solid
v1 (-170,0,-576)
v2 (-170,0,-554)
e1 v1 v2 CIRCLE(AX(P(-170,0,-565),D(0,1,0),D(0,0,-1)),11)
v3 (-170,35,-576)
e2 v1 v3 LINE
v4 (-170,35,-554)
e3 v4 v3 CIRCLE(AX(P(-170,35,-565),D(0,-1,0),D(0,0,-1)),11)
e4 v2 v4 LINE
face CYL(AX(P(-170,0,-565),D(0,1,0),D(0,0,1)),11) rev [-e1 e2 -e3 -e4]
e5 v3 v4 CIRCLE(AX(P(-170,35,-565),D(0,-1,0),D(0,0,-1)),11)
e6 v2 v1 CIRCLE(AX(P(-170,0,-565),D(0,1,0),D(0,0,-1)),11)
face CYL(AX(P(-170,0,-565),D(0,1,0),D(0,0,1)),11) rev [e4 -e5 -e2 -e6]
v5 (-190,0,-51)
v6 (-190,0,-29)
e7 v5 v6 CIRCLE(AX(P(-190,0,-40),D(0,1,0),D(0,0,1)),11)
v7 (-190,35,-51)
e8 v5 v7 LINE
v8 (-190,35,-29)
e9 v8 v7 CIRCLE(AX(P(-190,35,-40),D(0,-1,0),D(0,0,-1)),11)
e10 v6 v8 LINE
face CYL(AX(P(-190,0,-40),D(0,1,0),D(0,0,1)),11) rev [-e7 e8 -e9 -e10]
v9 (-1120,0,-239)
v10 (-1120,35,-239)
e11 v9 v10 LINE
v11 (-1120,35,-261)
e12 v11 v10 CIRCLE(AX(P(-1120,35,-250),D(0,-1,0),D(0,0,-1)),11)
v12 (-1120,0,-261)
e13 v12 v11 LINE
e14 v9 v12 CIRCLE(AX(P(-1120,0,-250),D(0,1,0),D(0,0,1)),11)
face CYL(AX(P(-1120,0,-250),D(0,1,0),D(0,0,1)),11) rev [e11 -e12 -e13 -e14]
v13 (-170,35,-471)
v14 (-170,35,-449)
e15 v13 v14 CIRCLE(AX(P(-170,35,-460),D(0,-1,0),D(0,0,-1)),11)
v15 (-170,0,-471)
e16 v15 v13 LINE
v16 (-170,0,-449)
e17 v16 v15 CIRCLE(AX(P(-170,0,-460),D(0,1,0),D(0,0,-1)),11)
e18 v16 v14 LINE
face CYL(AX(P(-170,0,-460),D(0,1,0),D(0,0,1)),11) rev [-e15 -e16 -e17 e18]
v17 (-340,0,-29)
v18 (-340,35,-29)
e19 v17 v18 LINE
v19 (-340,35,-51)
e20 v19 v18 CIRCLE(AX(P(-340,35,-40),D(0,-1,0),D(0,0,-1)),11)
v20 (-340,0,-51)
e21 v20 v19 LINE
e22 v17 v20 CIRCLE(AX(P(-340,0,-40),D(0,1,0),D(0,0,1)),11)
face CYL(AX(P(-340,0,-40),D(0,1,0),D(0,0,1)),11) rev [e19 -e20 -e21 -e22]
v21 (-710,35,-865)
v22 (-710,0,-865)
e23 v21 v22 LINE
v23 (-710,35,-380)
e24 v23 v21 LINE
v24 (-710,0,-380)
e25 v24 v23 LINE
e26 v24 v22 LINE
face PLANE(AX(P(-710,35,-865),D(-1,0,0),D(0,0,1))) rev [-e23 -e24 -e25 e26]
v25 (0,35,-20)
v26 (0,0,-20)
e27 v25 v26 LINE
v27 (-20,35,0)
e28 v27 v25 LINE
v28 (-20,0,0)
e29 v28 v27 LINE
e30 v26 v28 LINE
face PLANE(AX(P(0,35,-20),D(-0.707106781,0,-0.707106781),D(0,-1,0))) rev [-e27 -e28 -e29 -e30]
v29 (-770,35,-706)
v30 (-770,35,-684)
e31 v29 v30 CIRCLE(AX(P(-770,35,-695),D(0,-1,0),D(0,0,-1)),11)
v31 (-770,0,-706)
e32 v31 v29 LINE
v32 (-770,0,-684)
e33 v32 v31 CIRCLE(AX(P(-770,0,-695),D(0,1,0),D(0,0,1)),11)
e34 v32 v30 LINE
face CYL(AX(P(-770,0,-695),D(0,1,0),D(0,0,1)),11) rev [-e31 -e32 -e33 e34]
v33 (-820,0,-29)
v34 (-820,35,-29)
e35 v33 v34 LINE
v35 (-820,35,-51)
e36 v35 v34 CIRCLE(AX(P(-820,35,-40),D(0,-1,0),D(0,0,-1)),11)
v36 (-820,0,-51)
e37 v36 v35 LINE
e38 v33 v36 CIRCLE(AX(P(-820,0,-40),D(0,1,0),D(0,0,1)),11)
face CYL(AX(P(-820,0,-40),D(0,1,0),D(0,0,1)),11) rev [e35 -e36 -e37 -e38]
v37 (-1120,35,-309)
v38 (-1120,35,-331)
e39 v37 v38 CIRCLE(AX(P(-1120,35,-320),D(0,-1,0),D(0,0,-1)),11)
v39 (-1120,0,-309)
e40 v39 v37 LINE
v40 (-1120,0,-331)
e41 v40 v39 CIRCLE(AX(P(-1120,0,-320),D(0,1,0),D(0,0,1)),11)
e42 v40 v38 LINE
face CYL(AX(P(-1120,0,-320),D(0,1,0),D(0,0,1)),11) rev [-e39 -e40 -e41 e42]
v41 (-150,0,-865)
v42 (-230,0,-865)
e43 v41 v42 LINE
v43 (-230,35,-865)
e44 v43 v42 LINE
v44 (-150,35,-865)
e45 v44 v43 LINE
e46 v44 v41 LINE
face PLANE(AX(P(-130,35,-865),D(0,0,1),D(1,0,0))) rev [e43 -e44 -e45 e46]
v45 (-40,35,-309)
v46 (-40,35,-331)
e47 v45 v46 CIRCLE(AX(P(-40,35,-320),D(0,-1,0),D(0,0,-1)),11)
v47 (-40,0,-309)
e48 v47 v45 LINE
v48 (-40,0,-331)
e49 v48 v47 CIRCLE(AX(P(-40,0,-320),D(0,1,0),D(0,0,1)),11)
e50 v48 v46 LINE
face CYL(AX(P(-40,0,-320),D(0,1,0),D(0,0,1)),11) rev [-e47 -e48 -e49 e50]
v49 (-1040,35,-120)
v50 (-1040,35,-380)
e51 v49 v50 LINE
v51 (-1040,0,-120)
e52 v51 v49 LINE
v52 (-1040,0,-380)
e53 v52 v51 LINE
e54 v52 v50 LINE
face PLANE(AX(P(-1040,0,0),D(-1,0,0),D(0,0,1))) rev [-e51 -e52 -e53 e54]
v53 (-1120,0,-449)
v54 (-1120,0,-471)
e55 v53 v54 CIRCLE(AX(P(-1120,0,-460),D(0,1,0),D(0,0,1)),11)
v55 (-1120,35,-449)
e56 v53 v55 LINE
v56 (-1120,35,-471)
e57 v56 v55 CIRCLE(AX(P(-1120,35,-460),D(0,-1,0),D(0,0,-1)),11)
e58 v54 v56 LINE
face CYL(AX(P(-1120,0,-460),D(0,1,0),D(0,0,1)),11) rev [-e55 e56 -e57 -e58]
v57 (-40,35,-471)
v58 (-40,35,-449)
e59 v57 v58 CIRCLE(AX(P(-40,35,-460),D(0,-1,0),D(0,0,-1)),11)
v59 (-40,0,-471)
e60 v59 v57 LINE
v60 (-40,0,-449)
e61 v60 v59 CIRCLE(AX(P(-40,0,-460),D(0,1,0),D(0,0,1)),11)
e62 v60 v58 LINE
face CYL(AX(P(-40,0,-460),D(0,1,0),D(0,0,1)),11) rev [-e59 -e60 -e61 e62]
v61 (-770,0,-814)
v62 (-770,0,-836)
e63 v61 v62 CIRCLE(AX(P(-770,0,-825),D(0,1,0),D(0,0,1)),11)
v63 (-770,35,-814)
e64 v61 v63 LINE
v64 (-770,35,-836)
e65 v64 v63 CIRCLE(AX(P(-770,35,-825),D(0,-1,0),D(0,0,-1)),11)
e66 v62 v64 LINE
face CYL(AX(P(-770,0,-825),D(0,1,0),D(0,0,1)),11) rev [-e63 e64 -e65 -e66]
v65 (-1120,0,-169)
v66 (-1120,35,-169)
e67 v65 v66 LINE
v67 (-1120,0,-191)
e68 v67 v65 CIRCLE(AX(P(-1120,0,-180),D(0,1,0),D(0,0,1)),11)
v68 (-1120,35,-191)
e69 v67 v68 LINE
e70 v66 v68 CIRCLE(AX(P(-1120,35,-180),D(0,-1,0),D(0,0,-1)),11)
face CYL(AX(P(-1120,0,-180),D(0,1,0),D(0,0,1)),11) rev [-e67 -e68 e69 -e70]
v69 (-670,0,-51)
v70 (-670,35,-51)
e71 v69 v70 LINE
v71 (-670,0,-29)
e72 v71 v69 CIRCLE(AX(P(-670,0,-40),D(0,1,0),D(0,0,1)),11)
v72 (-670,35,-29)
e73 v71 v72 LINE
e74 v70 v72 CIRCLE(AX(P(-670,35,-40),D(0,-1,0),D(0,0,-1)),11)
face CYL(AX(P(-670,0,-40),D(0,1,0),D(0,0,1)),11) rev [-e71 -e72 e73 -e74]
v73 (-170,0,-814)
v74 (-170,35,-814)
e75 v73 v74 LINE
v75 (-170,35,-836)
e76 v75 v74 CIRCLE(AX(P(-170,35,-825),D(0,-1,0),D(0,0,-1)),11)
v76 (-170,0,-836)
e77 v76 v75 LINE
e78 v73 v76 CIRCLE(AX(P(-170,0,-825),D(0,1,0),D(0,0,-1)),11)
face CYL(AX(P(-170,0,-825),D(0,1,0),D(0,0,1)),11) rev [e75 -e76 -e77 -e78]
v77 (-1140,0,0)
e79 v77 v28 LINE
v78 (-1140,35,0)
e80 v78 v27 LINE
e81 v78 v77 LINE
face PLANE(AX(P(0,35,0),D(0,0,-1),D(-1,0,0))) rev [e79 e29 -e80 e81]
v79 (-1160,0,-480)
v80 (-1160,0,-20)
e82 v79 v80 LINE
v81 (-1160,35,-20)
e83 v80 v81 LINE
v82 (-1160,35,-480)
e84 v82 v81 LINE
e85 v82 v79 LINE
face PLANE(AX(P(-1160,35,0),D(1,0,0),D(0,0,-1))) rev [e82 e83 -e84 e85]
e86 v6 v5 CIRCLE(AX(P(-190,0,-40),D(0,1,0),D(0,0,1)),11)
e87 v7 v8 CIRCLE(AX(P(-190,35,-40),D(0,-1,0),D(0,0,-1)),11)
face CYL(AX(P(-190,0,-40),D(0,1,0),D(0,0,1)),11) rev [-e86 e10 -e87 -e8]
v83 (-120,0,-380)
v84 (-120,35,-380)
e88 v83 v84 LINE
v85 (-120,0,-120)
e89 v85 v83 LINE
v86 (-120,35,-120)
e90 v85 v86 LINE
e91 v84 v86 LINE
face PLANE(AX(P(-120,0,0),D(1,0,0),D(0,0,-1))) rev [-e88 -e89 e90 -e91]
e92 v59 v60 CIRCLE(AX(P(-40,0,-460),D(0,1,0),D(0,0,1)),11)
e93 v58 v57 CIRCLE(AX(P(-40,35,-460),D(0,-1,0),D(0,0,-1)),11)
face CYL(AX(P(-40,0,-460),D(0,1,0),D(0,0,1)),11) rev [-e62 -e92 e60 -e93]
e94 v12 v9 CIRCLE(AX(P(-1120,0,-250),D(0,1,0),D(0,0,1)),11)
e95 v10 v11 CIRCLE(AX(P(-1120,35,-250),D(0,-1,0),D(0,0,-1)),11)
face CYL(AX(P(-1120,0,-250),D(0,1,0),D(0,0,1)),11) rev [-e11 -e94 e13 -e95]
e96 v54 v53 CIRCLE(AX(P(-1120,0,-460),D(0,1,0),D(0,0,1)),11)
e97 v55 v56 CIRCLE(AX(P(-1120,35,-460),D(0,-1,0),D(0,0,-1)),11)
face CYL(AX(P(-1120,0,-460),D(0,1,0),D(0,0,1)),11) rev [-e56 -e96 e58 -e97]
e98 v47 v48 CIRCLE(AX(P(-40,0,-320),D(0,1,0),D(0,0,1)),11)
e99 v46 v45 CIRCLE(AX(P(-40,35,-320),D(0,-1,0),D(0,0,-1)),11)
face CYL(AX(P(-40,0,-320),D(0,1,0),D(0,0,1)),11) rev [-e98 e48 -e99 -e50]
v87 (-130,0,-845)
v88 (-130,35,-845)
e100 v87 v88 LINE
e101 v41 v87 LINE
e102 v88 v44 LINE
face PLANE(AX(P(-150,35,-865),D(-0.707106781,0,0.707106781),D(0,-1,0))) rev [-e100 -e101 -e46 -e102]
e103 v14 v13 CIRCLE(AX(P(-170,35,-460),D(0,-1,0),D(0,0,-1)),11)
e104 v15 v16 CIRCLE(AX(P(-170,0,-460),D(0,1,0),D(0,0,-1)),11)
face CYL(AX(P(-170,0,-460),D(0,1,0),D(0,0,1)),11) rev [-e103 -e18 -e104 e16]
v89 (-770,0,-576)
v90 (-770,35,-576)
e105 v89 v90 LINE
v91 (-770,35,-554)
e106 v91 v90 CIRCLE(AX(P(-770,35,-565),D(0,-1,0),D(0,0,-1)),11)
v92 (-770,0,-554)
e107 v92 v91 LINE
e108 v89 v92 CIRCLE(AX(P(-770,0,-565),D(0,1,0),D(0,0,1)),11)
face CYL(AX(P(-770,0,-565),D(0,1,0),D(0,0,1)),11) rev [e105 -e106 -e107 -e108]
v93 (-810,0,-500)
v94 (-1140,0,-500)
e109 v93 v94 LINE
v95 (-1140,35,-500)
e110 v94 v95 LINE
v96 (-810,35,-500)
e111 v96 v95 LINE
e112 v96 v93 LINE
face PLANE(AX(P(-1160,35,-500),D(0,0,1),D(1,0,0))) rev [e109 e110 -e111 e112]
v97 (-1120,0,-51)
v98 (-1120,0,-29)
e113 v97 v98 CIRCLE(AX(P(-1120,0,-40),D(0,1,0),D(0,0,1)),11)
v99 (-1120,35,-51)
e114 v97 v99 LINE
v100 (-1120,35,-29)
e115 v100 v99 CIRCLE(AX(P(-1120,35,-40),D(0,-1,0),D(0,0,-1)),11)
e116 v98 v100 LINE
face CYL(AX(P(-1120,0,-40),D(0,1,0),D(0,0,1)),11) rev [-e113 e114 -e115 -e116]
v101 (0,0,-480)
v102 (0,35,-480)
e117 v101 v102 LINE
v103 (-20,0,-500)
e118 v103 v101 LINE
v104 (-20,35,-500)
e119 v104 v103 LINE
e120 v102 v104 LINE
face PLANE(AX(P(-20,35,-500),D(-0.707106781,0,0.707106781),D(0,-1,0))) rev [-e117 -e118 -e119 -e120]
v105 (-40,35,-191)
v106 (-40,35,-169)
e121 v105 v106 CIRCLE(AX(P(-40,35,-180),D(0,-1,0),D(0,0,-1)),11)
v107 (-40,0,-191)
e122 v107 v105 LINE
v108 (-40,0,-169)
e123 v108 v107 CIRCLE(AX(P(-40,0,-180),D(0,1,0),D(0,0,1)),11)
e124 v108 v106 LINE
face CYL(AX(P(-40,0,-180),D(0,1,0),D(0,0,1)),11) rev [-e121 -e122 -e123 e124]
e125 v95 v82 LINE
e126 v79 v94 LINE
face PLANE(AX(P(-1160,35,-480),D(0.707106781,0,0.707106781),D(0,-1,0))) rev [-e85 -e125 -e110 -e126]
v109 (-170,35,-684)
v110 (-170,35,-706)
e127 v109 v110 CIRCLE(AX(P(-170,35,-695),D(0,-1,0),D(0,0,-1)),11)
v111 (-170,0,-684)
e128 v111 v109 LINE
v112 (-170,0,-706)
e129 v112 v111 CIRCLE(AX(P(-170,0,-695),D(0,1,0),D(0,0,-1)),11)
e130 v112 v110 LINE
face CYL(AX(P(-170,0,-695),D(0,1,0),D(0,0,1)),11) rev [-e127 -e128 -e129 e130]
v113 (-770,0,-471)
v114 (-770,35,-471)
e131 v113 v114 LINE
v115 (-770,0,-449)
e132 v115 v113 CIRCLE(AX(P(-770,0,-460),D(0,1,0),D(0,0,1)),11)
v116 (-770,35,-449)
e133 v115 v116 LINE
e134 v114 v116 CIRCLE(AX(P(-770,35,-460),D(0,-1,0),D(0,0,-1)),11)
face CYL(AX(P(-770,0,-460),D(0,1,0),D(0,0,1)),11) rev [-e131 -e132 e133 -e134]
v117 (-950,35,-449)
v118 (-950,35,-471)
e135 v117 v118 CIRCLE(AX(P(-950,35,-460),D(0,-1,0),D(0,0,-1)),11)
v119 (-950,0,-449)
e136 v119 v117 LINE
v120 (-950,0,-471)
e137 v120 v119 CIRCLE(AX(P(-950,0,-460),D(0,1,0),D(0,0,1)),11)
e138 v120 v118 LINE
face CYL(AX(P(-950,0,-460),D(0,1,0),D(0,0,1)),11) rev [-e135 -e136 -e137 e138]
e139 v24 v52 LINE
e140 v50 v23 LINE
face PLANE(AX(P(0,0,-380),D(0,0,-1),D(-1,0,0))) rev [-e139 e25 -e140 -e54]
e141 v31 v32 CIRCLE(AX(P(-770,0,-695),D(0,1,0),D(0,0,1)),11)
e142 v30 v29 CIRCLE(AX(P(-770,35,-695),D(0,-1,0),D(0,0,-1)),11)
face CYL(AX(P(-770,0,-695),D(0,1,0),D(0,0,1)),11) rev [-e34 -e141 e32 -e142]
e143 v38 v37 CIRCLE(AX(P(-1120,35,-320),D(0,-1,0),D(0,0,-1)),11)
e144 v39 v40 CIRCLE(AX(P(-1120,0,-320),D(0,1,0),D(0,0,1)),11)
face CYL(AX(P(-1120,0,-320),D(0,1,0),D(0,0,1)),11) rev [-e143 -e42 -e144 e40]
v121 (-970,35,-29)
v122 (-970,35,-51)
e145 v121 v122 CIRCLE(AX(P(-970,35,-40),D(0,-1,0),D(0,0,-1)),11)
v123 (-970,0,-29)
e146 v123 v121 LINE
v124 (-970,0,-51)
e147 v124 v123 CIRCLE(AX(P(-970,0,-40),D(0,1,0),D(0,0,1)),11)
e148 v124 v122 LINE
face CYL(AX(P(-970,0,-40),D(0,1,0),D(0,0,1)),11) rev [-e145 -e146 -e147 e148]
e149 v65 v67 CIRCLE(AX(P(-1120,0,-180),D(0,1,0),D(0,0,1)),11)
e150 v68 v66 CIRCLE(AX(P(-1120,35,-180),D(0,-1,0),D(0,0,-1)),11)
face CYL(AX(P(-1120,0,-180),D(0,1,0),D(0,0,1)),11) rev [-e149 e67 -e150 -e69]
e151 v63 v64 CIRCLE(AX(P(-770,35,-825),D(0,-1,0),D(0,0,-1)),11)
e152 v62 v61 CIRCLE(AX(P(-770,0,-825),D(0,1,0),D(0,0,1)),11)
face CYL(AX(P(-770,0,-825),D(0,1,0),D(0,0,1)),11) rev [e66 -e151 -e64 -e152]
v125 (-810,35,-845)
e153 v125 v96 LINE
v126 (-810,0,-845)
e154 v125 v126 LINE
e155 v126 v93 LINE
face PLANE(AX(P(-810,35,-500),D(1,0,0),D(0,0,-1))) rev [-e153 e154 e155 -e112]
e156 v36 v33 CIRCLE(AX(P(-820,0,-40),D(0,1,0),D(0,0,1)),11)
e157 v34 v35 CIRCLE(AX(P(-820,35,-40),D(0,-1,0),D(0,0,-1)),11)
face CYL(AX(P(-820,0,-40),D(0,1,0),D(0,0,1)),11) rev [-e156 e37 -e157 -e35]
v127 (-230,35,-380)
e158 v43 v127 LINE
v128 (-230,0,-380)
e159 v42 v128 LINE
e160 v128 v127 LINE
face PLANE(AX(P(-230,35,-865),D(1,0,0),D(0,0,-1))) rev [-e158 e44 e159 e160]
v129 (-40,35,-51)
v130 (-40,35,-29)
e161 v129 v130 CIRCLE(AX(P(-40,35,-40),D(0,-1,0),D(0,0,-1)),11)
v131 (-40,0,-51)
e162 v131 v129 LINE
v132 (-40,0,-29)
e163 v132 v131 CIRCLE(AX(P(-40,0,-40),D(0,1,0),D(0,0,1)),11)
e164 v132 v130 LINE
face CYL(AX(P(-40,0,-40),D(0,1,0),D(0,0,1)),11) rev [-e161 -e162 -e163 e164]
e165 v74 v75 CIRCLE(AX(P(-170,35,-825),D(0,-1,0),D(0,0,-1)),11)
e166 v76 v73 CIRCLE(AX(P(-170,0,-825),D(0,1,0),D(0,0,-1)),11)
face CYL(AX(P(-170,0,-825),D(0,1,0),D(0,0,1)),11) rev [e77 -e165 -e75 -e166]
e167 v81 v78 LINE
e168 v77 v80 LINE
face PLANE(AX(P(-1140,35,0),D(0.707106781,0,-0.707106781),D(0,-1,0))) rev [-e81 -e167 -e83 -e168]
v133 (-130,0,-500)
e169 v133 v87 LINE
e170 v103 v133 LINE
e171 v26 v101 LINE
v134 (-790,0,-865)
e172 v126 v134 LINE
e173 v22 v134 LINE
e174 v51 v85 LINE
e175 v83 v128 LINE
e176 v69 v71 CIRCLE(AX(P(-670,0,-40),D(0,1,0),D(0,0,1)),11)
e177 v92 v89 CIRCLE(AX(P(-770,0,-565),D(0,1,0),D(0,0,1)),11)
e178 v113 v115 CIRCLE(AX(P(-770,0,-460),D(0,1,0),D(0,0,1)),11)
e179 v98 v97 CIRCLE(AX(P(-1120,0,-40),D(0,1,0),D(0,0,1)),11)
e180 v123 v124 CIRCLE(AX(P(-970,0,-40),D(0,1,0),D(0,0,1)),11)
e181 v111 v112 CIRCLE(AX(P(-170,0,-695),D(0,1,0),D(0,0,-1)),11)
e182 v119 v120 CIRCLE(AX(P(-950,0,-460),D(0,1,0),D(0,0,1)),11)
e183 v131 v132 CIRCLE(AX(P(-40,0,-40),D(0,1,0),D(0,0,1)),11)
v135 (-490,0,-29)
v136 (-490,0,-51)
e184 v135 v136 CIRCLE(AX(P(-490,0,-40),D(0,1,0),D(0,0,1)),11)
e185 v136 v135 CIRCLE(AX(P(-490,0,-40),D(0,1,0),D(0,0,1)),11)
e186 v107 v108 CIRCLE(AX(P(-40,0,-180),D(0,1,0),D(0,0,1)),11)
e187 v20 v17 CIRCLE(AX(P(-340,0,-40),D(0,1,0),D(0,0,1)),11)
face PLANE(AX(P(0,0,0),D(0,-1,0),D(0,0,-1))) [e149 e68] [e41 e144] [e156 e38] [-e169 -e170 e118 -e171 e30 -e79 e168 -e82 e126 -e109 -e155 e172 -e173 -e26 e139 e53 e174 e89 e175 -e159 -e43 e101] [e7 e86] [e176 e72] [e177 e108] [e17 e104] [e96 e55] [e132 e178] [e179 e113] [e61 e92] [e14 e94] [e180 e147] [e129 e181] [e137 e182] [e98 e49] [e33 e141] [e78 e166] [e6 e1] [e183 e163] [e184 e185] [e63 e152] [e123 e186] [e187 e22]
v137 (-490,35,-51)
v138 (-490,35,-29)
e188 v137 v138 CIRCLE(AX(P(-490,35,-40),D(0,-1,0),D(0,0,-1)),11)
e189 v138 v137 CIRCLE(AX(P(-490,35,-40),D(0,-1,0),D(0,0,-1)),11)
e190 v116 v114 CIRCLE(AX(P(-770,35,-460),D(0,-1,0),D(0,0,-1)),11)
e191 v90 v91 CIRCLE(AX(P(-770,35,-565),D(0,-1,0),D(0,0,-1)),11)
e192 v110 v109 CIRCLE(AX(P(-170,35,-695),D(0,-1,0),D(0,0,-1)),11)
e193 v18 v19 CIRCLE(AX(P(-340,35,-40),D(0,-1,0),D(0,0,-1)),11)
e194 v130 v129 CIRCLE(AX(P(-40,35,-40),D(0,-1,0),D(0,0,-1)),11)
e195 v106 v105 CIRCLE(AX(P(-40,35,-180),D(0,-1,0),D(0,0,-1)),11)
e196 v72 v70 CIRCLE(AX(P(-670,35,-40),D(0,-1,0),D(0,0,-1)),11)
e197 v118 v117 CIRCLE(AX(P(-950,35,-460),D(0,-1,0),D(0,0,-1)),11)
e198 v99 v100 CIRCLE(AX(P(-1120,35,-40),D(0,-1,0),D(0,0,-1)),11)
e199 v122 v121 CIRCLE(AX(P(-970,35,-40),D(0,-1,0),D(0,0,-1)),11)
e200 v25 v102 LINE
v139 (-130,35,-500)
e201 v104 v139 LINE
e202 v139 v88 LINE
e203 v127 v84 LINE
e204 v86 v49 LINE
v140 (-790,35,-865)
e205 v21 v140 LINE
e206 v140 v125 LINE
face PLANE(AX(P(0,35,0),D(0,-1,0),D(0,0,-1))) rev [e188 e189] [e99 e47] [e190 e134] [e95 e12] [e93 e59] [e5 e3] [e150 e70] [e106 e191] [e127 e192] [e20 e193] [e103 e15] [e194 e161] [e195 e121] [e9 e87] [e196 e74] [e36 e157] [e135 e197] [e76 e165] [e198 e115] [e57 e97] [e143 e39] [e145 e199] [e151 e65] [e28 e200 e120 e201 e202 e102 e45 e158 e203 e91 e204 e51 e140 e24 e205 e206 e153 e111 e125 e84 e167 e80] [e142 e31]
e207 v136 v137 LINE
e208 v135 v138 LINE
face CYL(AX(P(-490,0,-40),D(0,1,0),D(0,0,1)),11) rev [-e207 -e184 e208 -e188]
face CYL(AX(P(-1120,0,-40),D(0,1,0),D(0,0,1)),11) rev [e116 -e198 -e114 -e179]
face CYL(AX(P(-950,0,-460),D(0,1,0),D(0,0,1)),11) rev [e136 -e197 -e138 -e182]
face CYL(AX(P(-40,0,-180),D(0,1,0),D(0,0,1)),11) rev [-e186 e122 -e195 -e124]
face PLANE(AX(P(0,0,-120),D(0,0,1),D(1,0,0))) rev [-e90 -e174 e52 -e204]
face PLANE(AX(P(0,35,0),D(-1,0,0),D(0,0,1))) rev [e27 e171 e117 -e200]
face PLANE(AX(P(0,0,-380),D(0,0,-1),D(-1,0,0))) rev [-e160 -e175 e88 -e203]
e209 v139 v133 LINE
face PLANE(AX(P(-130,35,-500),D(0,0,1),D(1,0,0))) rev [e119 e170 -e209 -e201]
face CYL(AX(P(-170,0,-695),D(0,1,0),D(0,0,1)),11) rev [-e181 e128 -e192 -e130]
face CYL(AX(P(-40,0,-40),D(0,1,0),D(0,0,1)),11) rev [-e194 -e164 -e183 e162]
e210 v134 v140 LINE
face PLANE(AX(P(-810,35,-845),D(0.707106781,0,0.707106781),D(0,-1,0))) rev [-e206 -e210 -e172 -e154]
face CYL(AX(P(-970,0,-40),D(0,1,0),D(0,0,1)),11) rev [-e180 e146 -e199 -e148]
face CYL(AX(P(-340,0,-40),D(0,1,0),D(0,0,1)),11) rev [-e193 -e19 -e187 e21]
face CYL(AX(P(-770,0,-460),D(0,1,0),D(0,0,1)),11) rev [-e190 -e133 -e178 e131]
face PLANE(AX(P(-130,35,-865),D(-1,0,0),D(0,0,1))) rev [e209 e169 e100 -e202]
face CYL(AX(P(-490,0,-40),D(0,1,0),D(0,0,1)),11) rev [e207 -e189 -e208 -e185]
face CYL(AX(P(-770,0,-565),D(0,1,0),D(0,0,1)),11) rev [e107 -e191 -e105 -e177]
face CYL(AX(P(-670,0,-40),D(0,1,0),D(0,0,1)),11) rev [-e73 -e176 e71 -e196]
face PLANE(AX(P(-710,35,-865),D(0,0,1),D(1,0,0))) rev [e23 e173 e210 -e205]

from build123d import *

# Parameters (mm, degrees)
BOSS_EXTRUDE1_DEPTH     = 35
CUT_EXTRUDE1_DEPTH      = 1448.428754723
CUT_EXTRUDE1_DEPTH_BACK = 1448.428754723
CHAMFER2_SIZE           = 20
CUT_EXTRUDE2_DEPTH      = 1448.428754723
CUT_EXTRUDE2_DEPTH_BACK = 1448.428754723
SKETCH5_R               = 11


with BuildPart() as part:
    # Sketch1 → Boss-Extrude1 (new body)
    with BuildSketch(Plane(origin=(0, 0, 0), x_dir=(1, 0, 0), z_dir=(0, 1, 0))):
        Polygon((-1160, 500), (-810, 500), (-810, 865), (-710, 865), (-710, 745), (-230, 745), (-230, 865), (-130, 865), (-130, 500), (0, 500), (0, 0), (-1160, 0), align=None)
    extrude(amount=BOSS_EXTRUDE1_DEPTH)

    # Sketch4 → Cut-Extrude1 (cut, two sides: drawn at the far end of the back side and taken through both)
    with BuildSketch(Plane(origin=(0, 35, 0), x_dir=(1, 0, 0), z_dir=(0, 1, 0)).offset(-CUT_EXTRUDE1_DEPTH_BACK)):
        Polygon((-230, 745), (-710, 745), (-710, 380), (-1040, 380), (-1040, 120), (-120, 120), (-120, 380), (-230, 380), align=None)
    extrude(amount=CUT_EXTRUDE1_DEPTH + CUT_EXTRUDE1_DEPTH_BACK, mode=Mode.SUBTRACT)

    # Chamfer2
    chamfer2_edges = [part.edges().sort_by_distance(p)[0] for p in [
        (0, 17.5, 0),
        (-1160, 17.5, 0),
        (-1160, 17.5, -500),
        (-810, 17.5, -865),
        (-130, 17.5, -865),
        (0, 17.5, -500),
    ]]
    chamfer(chamfer2_edges, length=CHAMFER2_SIZE)

    # Sketch5 → Cut-Extrude2 (cut, two sides: drawn at the far end of the back side and taken through both)
    with BuildSketch(Plane(origin=(0, 35, 0), x_dir=(1, 0, 0), z_dir=(0, 1, 0)).offset(-CUT_EXTRUDE2_DEPTH_BACK)):
        with Locations(Location((-1120, 40, 0), (0, 0, 270))):
            Circle(SKETCH5_R)
        with Locations(Location((-970, 40, 0), (0, 0, 270))):
            Circle(SKETCH5_R)
        with Locations(Location((-820, 40, 0), (0, 0, 270))):
            Circle(SKETCH5_R)
        with Locations(Location((-670, 40, 0), (0, 0, 270))):
            Circle(SKETCH5_R)
        with Locations(Location((-490, 40, 0), (0, 0, 270))):
            Circle(SKETCH5_R)
        with Locations(Location((-340, 40, 0), (0, 0, 270))):
            Circle(SKETCH5_R)
        with Locations(Location((-190, 40, 0), (0, 0, 270))):
            Circle(SKETCH5_R)
        with Locations(Location((-40, 40, 0), (0, 0, 270))):
            Circle(SKETCH5_R)
        with Locations(Location((-770, 825, 0), (0, 0, 270))):
            Circle(SKETCH5_R)
        with Locations(Location((-770, 695, 0), (0, 0, 270))):
            Circle(SKETCH5_R)
        with Locations(Location((-770, 565, 0), (0, 0, 270))):
            Circle(SKETCH5_R)
        with Locations(Location((-770, 460, 0), (0, 0, 270))):
            Circle(SKETCH5_R)
        with Locations(Location((-1120, 180, 0), (0, 0, 270))):
            Circle(SKETCH5_R)
        with Locations(Location((-1120, 250, 0), (0, 0, 270))):
            Circle(SKETCH5_R)
        with Locations(Location((-1120, 320, 0), (0, 0, 270))):
            Circle(SKETCH5_R)
        with Locations(Location((-1120, 460, 0), (0, 0, 270))):
            Circle(SKETCH5_R)
        with Locations(Location((-950, 460, 0), (0, 0, 270))):
            Circle(SKETCH5_R)
        with Locations(Location((-170, 460, 0), (0, 0, 90))):
            Circle(SKETCH5_R)
        with Locations(Location((-170, 565, 0), (0, 0, 90))):
            Circle(SKETCH5_R)
        with Locations(Location((-170, 695, 0), (0, 0, 90))):
            Circle(SKETCH5_R)
        with Locations(Location((-170, 825, 0), (0, 0, 90))):
            Circle(SKETCH5_R)
        with Locations(Location((-40, 460, 0), (0, 0, 270))):
            Circle(SKETCH5_R)
        with Locations(Location((-40, 320, 0), (0, 0, 270))):
            Circle(SKETCH5_R)
        with Locations(Location((-40, 180, 0), (0, 0, 270))):
            Circle(SKETCH5_R)
    extrude(amount=CUT_EXTRUDE2_DEPTH + CUT_EXTRUDE2_DEPTH_BACK, mode=Mode.SUBTRACT)


solid = part.part
